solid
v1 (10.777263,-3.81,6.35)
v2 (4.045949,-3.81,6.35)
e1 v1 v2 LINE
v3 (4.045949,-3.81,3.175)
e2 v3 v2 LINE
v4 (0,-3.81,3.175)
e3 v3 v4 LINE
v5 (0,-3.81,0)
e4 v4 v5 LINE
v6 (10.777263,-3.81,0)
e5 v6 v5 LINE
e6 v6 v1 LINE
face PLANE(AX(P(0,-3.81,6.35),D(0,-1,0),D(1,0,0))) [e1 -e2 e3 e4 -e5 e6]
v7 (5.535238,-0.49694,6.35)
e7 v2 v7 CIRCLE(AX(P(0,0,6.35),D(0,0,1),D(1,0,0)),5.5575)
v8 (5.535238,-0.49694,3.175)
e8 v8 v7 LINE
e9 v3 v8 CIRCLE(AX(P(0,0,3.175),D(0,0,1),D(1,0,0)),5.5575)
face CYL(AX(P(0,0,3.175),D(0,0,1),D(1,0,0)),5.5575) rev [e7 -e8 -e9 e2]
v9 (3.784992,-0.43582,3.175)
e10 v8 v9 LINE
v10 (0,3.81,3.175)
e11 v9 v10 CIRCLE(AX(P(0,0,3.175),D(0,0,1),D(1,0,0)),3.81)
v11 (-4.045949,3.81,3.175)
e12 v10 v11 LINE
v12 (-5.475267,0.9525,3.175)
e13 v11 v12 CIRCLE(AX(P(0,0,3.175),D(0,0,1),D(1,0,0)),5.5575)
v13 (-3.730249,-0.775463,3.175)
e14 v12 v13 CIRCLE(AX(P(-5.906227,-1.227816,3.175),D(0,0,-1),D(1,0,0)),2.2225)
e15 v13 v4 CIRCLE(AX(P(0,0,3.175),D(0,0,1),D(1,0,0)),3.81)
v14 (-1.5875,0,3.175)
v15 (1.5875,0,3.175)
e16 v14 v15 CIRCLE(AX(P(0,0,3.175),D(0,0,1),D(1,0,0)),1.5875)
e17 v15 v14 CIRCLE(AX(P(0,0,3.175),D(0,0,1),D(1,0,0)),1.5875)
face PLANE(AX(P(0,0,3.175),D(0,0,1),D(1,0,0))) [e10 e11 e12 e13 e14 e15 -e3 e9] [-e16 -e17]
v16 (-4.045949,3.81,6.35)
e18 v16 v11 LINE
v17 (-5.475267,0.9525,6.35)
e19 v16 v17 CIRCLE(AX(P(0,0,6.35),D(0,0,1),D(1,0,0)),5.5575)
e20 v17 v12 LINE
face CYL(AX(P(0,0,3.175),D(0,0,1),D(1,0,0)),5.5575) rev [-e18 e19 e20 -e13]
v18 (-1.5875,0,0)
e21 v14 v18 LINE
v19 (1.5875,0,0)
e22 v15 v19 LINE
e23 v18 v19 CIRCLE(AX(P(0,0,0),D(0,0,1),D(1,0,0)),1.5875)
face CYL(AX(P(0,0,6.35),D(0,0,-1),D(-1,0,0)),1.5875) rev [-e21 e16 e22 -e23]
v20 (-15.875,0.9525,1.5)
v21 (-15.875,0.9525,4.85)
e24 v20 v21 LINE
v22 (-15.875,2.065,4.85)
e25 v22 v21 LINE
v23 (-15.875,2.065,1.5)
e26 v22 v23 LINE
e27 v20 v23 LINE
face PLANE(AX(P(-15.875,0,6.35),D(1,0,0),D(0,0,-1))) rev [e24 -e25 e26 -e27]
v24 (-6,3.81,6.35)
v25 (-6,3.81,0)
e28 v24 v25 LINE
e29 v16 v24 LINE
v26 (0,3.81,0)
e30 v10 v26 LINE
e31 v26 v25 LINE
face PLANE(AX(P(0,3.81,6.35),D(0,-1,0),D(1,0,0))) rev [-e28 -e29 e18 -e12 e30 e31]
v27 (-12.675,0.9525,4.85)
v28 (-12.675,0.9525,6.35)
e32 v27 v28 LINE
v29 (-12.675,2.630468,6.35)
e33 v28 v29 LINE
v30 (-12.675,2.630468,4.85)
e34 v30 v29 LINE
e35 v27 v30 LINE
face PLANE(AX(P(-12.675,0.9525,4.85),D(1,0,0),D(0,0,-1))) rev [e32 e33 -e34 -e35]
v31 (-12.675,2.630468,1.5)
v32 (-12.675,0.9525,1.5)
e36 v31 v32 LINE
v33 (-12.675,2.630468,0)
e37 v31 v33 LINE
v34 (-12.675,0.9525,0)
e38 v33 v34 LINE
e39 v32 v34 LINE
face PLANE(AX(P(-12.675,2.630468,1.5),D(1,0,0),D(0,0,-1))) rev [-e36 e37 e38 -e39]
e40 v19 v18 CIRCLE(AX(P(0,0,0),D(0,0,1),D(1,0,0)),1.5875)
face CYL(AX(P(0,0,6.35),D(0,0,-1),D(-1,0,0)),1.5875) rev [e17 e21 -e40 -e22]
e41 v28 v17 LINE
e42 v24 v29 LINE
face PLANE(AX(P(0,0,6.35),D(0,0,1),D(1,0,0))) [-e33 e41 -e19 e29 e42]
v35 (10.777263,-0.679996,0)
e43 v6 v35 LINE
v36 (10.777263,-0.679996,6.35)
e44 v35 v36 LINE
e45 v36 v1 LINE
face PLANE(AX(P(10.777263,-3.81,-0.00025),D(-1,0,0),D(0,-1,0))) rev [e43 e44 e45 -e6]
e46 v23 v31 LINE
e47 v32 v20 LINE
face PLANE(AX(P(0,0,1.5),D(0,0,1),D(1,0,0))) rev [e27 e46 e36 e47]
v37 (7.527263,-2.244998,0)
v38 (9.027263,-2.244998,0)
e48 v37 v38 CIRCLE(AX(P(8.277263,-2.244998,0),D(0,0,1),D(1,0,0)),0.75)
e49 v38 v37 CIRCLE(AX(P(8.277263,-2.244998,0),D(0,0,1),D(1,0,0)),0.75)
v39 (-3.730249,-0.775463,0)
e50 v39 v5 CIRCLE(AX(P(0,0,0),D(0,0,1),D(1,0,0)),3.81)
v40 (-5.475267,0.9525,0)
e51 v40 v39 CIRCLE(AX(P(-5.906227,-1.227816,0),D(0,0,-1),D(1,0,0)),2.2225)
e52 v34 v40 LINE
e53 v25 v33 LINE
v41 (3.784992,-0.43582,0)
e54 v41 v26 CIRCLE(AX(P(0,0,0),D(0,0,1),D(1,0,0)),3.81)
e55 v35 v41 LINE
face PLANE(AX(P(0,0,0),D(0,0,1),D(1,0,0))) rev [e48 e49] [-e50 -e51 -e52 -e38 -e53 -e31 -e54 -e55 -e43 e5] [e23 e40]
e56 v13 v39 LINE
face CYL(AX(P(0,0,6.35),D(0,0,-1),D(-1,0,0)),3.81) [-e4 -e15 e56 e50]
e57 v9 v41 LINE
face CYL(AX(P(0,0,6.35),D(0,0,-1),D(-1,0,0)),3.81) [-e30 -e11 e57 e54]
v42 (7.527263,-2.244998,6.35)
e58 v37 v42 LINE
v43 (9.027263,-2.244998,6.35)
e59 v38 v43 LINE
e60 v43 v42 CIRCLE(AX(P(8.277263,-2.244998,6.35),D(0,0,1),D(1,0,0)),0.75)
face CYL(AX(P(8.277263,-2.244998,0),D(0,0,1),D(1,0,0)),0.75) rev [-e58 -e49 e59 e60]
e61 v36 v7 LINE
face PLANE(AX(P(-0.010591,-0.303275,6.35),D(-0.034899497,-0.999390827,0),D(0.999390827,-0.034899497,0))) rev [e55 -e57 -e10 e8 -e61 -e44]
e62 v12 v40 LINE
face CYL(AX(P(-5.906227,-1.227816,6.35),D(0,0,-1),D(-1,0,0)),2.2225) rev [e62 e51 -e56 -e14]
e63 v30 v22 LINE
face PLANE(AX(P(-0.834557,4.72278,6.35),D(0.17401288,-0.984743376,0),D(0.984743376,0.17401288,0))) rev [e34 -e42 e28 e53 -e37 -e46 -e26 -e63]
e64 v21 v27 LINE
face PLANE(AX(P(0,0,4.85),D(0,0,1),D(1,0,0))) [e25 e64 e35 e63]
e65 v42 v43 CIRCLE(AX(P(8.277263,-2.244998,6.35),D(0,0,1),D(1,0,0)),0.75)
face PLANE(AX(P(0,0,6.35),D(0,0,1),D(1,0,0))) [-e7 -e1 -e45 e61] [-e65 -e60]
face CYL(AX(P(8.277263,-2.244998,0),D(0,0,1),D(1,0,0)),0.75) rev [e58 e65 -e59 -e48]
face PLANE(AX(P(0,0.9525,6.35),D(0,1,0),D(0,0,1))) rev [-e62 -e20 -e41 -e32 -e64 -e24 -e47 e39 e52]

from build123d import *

# Parameters (mm, degrees)
SKETCH1_R           = 6.35
BOSS_EXTRUDE1_DEPTH = 25.4
SKETCH2_R           = 22.23
CUT_EXTRUDE1_DEPTH  = 12.7
CUT_EXTRUDE_1_REACH = 169.736
SCALE_1_SCALE       = 0.5
SCALE_2_SCALE       = 0.5
SKETCH_2_R          = 0.75
CUT_EXTRUDE_2_DEPTH = 18.517255065
SKETCH_3_W          = 3.175
SKETCH_3_H          = 0.9525
CUT_EXTRUDE_3_DEPTH = 6.35
CUT_EXTRUDE_4_DEPTH = 1.5
CUT_EXTRUDE_5_DEPTH = 1.5


with BuildPart() as part:
    # Sketch1 → Boss-Extrude1 (new body)
    with BuildSketch(Plane.XY):
        with BuildLine():
            Line((0, -15.24), (165.1, -15.24))
            Line((165.1, -15.24), (165.1, -6.98))
            Line((165.1, -6.98), (27.790517271, -2.185047205))
            Line((27.790517271, -2.185047205), (22.140950977, -1.987760002))
            Line((22.140950977, -1.987760002), (15.139966118, -1.743280224))
            ThreePointArc((15.139966118, -1.743280224), (11.375965687, 10.14125262), (0, 15.24))
            Line((0, 15.24), (-24, 15.24))
            Line((-24, 15.24), (-63.5, 8.26))
            Line((-63.5, 8.26), (-63.5, 0))
            Line((-63.5, 0), (-50.8, 0))
            Line((-50.8, 0), (-50.8, 3.81))
            Line((-50.8, 3.81), (-46.99, 3.81))
            Line((-46.99, 3.81), (-21.901068467, 3.81))
            ThreePointArc((-21.901068467, 3.81), (-17.369676473, 1.405708043), (-14.920995783, -3.10185184))
            ThreePointArc((-14.920995783, -3.10185184), (-9.617311942, -11.82222107), (0, -15.24))
        make_face()
        Circle(SKETCH1_R, mode=Mode.SUBTRACT)
    extrude(amount=BOSS_EXTRUDE1_DEPTH)

    # Sketch2 → Cut-Extrude1 (cut)
    with BuildSketch(Plane.XY.offset(25.4)):
        Circle(SKETCH2_R)
    extrude(amount=-CUT_EXTRUDE1_DEPTH, mode=Mode.SUBTRACT)

    # 草图1 → 切除-拉伸1 (cut, up to next)
    with BuildSketch(Plane.XY.offset(25.4), mode=Mode.PRIVATE) as cut_extrude_1_sk1:
        Polygon((43.109053356, -15.24), (43.109053356, -2.719982272), (165.1, -6.98), (165.1, -15.24), align=None)
    cut_extrude_1_tool1 = extrude(cut_extrude_1_sk1.sketch, amount=-CUT_EXTRUDE_1_REACH, mode=Mode.PRIVATE) & part.part
    add(cut_extrude_1_tool1.solids().sort_by_distance((99.936391, -9.972218, 25.4))[0], mode=Mode.SUBTRACT)


with BuildPart() as part_1:
    # 缩放比例1: scaled about (0, 0, 0)
    add(part.part.scale(SCALE_1_SCALE))


with BuildPart() as part_2:
    # 缩放比例2: scaled about (0, 0, 0)
    add(part_1.part.scale(SCALE_2_SCALE))

    # 草图2 → 切除-拉伸2 (cut, through all)
    with BuildSketch(Plane.XY.offset(6.35)):
        with Locations((8.277263339, -2.244997784)):
            Circle(SKETCH_2_R)
    extrude(amount=-CUT_EXTRUDE_2_DEPTH, mode=Mode.SUBTRACT)

    # 草图3 → 切除-拉伸3 (cut)
    with BuildSketch(Plane.XY.offset(6.35)):
        with Locations((-14.2875, 0.47625)):
            Rectangle(SKETCH_3_W, SKETCH_3_H)
    extrude(amount=-CUT_EXTRUDE_3_DEPTH, mode=Mode.SUBTRACT)

    # 草图4 → 切除-拉伸4 (cut)
    with BuildSketch(Plane.XY.offset(6.35)):
        Polygon((-15.875, 2.065), (-15.875, 0.9525), (-12.675, 0.9525), (-12.675, 2.630468354), align=None)
    extrude(amount=-CUT_EXTRUDE_4_DEPTH, mode=Mode.SUBTRACT)

    # 草图5 → 切除-拉伸5 (cut)
    with BuildSketch(Plane(origin=(0, 0, 0), x_dir=(-1, 0, 0), z_dir=(0, 0, -1))):
        Polygon((15.875, 2.065), (15.875, 0.9525), (12.675, 0.9525), (12.675, 2.630468354), align=None)
    extrude(amount=-CUT_EXTRUDE_5_DEPTH, mode=Mode.SUBTRACT)


solid = part_2.part
